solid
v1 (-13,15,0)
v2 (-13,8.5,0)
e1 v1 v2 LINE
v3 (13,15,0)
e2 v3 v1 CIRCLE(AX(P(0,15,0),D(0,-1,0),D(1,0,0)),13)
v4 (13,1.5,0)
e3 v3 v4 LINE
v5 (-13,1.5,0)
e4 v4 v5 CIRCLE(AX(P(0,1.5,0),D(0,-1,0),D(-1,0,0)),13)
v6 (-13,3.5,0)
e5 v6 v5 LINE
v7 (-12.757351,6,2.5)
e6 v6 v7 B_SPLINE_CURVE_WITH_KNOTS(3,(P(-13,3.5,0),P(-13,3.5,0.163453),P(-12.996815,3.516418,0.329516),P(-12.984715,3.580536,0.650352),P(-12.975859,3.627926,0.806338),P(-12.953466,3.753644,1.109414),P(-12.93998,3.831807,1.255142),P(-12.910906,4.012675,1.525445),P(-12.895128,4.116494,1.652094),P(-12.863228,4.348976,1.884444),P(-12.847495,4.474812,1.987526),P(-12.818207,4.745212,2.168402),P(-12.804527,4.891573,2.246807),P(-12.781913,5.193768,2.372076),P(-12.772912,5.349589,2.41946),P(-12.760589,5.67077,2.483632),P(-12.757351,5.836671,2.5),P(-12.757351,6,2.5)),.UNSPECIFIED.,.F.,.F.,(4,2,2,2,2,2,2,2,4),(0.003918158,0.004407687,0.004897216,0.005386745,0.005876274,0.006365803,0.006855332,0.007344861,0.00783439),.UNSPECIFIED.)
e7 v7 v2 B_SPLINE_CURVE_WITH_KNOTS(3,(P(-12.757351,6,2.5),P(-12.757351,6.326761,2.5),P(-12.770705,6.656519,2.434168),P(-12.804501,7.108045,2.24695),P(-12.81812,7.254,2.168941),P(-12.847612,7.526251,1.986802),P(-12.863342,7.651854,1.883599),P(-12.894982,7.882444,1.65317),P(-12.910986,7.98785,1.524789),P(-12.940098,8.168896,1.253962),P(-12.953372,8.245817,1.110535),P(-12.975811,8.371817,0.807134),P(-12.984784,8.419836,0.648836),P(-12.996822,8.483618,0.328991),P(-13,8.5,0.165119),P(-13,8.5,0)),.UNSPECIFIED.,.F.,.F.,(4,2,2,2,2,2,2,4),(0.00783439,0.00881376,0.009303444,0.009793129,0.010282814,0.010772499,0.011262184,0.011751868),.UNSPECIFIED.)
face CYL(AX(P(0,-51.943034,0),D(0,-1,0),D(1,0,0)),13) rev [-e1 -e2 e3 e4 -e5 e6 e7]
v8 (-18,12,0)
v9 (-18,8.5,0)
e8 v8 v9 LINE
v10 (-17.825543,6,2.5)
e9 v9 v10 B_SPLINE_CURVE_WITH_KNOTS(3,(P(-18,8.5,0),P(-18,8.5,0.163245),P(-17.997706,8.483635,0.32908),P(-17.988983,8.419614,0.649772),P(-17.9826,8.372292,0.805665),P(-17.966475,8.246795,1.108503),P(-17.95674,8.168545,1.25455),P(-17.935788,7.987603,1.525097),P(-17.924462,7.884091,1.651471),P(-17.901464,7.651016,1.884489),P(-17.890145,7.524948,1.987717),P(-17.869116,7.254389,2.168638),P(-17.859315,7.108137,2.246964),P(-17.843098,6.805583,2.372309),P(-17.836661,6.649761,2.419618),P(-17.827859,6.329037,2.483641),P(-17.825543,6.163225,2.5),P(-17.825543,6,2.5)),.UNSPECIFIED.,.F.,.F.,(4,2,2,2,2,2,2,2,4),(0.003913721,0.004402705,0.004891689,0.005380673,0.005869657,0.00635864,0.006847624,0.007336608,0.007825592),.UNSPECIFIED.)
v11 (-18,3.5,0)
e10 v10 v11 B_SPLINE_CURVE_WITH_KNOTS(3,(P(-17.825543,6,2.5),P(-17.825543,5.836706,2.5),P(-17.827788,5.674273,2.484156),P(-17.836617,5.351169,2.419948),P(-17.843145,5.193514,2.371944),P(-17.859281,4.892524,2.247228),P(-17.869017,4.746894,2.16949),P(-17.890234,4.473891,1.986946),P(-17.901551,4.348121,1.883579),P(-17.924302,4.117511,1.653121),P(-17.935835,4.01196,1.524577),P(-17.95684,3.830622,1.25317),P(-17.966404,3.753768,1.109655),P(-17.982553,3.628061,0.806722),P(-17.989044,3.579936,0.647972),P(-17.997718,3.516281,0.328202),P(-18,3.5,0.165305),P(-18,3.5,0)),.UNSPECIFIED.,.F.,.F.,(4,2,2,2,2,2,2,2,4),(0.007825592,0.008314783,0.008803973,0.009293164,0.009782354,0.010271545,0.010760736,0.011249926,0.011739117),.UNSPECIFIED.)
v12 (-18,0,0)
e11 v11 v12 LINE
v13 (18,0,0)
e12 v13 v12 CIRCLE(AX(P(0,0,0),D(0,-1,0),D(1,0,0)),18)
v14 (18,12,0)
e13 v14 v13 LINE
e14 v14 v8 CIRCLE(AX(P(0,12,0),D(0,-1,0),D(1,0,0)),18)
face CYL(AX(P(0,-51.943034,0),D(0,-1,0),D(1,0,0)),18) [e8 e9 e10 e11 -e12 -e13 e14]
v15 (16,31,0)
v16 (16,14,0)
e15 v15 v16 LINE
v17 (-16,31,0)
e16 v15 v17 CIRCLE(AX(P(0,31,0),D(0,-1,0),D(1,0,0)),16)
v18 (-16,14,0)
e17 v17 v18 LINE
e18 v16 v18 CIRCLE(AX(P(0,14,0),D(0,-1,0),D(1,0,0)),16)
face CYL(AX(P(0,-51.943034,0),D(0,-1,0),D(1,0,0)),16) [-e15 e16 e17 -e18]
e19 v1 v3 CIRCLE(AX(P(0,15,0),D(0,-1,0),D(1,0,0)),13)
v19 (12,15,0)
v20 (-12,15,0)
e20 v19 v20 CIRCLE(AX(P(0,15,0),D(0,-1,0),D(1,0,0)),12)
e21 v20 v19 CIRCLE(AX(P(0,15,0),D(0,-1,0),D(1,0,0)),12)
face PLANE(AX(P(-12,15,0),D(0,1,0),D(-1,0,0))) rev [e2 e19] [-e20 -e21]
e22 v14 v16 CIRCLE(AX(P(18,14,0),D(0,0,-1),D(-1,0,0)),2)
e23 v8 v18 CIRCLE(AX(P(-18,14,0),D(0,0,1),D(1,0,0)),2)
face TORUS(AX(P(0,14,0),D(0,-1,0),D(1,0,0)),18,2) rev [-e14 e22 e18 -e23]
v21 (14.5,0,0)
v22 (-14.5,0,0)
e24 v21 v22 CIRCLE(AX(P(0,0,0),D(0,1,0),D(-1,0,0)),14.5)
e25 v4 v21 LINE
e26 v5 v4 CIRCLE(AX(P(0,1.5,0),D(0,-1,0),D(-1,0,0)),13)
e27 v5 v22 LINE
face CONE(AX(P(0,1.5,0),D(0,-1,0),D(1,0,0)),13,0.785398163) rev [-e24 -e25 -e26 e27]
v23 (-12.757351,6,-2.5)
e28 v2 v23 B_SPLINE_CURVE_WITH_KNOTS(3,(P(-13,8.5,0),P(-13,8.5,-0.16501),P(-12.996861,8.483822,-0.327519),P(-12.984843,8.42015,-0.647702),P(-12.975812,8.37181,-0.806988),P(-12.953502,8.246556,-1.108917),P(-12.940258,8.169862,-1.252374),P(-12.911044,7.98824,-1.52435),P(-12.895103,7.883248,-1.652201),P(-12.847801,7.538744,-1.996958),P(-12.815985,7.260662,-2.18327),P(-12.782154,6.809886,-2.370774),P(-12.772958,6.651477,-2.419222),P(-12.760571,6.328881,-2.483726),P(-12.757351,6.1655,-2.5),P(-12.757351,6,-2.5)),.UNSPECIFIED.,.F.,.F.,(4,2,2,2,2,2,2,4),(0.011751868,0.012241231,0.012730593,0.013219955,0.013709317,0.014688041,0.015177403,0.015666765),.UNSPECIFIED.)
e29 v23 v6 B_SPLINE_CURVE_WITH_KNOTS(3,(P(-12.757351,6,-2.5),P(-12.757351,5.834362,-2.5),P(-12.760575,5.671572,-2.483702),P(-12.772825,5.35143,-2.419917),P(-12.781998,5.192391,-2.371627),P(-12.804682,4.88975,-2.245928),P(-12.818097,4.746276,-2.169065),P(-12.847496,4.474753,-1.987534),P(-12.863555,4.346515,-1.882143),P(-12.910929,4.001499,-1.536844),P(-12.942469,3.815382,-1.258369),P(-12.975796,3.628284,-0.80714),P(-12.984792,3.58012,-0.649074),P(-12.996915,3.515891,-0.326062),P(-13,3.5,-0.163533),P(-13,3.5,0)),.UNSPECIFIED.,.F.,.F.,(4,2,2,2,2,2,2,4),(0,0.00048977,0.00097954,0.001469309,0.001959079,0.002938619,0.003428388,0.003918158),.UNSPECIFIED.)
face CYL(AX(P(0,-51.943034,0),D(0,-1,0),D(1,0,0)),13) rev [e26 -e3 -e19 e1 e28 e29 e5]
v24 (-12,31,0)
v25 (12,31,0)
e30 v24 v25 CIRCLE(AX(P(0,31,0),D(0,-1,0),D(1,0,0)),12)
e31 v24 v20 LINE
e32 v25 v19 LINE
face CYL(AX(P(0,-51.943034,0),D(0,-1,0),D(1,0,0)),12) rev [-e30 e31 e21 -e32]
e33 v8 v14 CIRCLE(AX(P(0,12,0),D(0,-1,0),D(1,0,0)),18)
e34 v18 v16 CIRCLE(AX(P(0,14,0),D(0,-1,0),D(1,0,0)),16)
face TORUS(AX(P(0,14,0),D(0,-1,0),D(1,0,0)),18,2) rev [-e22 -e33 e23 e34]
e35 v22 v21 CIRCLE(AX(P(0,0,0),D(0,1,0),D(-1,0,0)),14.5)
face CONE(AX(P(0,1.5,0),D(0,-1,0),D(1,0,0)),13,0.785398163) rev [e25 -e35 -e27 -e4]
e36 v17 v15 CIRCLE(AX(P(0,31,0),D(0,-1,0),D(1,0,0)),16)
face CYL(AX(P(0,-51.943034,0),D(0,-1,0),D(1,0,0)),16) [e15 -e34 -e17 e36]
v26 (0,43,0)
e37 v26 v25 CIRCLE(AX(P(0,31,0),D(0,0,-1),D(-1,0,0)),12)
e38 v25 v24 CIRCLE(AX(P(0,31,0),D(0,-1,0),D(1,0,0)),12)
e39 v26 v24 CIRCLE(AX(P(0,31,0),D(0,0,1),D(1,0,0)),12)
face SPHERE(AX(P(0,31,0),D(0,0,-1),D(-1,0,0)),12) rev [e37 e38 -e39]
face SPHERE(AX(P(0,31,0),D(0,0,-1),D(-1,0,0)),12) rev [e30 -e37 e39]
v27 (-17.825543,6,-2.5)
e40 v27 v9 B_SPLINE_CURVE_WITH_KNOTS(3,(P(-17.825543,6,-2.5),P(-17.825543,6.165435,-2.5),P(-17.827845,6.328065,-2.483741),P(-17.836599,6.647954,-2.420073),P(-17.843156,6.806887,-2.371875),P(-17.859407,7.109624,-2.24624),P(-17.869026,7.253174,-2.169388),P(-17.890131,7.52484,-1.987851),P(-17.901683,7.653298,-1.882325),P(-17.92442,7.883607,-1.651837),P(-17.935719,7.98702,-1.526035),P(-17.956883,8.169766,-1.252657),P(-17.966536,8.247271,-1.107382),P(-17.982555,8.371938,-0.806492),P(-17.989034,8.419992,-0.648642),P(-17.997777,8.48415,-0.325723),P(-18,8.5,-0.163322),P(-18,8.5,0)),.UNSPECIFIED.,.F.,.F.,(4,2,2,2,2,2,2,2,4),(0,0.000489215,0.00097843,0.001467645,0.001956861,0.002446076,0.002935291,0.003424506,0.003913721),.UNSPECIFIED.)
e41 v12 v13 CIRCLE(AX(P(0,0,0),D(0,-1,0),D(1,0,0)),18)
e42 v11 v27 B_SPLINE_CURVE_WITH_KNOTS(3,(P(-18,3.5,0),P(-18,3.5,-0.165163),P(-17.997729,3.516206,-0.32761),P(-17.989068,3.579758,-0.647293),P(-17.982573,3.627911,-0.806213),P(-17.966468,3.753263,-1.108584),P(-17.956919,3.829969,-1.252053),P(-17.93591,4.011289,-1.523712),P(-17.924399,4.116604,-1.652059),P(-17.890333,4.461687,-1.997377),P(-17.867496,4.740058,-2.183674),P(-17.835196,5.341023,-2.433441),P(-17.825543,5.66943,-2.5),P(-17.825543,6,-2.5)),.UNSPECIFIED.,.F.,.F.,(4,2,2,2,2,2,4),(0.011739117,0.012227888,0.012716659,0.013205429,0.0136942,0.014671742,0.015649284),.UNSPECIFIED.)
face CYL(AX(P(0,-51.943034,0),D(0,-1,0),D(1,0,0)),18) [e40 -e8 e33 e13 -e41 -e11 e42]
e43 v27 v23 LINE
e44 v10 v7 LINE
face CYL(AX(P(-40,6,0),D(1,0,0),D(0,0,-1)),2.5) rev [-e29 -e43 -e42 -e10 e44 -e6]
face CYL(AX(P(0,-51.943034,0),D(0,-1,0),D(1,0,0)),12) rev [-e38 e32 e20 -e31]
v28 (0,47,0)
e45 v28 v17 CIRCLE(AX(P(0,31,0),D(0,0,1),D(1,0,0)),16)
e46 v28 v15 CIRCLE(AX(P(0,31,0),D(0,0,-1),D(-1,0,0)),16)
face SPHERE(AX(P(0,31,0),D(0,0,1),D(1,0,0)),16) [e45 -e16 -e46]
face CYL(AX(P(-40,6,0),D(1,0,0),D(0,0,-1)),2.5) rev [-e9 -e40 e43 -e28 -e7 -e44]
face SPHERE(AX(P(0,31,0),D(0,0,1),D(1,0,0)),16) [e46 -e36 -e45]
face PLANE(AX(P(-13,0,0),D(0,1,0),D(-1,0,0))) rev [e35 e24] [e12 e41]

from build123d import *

# Parameters (mm, degrees)
SKETCH3_R          = 2.5
CUT_EXTRUDE1_DEPTH = 40
CHAMFER1_SIZE      = 1.5


with BuildPart() as part:
    # Sketch2 → Revolve1 (revolve)
    with BuildSketch(Plane.XY, mode=Mode.PRIVATE) as revolve1_sk:
        with BuildLine():
            Line((-16, 31), (-16, 14))
            ThreePointArc((-16, 14), (-16.585786438, 12.585786438), (-18, 12))
            Line((-18, 12), (-18, 0))
            Line((-18, 0), (-13, 0))
            Line((-13, 0), (-13, 15))
            Line((-13, 15), (-12, 15))
            Line((-12, 15), (-12, 31))
            ThreePointArc((-12, 31), (-8.485281374, 39.485281374), (0, 43))
            Line((0, 43), (0, 47))
            ThreePointArc((0, 47), (-11.313708499, 42.313708499), (-16, 31))
        make_face()
    revolve(revolve1_sk.sketch.rotate(Axis((0, -51.943033939, 0), (0, 1, 0)), 180), axis=Axis((0, -51.943033939, 0), (0, 1, 0)))

    # Sketch3 → Cut-Extrude1 (cut)
    with BuildSketch(Plane(origin=(0, 0, 0), x_dir=(0, 0, -1), z_dir=(1, 0, 0))):
        with Locations((0, 6)):
            Circle(SKETCH3_R)
    extrude(amount=-CUT_EXTRUDE1_DEPTH, mode=Mode.SUBTRACT)

    # Chamfer1
    chamfer1_edges = [part.edges().sort_by_distance(p)[0] for p in [
        (-13, 0, 0),
    ]]
    chamfer(chamfer1_edges, length=CHAMFER1_SIZE)


solid = part.part
